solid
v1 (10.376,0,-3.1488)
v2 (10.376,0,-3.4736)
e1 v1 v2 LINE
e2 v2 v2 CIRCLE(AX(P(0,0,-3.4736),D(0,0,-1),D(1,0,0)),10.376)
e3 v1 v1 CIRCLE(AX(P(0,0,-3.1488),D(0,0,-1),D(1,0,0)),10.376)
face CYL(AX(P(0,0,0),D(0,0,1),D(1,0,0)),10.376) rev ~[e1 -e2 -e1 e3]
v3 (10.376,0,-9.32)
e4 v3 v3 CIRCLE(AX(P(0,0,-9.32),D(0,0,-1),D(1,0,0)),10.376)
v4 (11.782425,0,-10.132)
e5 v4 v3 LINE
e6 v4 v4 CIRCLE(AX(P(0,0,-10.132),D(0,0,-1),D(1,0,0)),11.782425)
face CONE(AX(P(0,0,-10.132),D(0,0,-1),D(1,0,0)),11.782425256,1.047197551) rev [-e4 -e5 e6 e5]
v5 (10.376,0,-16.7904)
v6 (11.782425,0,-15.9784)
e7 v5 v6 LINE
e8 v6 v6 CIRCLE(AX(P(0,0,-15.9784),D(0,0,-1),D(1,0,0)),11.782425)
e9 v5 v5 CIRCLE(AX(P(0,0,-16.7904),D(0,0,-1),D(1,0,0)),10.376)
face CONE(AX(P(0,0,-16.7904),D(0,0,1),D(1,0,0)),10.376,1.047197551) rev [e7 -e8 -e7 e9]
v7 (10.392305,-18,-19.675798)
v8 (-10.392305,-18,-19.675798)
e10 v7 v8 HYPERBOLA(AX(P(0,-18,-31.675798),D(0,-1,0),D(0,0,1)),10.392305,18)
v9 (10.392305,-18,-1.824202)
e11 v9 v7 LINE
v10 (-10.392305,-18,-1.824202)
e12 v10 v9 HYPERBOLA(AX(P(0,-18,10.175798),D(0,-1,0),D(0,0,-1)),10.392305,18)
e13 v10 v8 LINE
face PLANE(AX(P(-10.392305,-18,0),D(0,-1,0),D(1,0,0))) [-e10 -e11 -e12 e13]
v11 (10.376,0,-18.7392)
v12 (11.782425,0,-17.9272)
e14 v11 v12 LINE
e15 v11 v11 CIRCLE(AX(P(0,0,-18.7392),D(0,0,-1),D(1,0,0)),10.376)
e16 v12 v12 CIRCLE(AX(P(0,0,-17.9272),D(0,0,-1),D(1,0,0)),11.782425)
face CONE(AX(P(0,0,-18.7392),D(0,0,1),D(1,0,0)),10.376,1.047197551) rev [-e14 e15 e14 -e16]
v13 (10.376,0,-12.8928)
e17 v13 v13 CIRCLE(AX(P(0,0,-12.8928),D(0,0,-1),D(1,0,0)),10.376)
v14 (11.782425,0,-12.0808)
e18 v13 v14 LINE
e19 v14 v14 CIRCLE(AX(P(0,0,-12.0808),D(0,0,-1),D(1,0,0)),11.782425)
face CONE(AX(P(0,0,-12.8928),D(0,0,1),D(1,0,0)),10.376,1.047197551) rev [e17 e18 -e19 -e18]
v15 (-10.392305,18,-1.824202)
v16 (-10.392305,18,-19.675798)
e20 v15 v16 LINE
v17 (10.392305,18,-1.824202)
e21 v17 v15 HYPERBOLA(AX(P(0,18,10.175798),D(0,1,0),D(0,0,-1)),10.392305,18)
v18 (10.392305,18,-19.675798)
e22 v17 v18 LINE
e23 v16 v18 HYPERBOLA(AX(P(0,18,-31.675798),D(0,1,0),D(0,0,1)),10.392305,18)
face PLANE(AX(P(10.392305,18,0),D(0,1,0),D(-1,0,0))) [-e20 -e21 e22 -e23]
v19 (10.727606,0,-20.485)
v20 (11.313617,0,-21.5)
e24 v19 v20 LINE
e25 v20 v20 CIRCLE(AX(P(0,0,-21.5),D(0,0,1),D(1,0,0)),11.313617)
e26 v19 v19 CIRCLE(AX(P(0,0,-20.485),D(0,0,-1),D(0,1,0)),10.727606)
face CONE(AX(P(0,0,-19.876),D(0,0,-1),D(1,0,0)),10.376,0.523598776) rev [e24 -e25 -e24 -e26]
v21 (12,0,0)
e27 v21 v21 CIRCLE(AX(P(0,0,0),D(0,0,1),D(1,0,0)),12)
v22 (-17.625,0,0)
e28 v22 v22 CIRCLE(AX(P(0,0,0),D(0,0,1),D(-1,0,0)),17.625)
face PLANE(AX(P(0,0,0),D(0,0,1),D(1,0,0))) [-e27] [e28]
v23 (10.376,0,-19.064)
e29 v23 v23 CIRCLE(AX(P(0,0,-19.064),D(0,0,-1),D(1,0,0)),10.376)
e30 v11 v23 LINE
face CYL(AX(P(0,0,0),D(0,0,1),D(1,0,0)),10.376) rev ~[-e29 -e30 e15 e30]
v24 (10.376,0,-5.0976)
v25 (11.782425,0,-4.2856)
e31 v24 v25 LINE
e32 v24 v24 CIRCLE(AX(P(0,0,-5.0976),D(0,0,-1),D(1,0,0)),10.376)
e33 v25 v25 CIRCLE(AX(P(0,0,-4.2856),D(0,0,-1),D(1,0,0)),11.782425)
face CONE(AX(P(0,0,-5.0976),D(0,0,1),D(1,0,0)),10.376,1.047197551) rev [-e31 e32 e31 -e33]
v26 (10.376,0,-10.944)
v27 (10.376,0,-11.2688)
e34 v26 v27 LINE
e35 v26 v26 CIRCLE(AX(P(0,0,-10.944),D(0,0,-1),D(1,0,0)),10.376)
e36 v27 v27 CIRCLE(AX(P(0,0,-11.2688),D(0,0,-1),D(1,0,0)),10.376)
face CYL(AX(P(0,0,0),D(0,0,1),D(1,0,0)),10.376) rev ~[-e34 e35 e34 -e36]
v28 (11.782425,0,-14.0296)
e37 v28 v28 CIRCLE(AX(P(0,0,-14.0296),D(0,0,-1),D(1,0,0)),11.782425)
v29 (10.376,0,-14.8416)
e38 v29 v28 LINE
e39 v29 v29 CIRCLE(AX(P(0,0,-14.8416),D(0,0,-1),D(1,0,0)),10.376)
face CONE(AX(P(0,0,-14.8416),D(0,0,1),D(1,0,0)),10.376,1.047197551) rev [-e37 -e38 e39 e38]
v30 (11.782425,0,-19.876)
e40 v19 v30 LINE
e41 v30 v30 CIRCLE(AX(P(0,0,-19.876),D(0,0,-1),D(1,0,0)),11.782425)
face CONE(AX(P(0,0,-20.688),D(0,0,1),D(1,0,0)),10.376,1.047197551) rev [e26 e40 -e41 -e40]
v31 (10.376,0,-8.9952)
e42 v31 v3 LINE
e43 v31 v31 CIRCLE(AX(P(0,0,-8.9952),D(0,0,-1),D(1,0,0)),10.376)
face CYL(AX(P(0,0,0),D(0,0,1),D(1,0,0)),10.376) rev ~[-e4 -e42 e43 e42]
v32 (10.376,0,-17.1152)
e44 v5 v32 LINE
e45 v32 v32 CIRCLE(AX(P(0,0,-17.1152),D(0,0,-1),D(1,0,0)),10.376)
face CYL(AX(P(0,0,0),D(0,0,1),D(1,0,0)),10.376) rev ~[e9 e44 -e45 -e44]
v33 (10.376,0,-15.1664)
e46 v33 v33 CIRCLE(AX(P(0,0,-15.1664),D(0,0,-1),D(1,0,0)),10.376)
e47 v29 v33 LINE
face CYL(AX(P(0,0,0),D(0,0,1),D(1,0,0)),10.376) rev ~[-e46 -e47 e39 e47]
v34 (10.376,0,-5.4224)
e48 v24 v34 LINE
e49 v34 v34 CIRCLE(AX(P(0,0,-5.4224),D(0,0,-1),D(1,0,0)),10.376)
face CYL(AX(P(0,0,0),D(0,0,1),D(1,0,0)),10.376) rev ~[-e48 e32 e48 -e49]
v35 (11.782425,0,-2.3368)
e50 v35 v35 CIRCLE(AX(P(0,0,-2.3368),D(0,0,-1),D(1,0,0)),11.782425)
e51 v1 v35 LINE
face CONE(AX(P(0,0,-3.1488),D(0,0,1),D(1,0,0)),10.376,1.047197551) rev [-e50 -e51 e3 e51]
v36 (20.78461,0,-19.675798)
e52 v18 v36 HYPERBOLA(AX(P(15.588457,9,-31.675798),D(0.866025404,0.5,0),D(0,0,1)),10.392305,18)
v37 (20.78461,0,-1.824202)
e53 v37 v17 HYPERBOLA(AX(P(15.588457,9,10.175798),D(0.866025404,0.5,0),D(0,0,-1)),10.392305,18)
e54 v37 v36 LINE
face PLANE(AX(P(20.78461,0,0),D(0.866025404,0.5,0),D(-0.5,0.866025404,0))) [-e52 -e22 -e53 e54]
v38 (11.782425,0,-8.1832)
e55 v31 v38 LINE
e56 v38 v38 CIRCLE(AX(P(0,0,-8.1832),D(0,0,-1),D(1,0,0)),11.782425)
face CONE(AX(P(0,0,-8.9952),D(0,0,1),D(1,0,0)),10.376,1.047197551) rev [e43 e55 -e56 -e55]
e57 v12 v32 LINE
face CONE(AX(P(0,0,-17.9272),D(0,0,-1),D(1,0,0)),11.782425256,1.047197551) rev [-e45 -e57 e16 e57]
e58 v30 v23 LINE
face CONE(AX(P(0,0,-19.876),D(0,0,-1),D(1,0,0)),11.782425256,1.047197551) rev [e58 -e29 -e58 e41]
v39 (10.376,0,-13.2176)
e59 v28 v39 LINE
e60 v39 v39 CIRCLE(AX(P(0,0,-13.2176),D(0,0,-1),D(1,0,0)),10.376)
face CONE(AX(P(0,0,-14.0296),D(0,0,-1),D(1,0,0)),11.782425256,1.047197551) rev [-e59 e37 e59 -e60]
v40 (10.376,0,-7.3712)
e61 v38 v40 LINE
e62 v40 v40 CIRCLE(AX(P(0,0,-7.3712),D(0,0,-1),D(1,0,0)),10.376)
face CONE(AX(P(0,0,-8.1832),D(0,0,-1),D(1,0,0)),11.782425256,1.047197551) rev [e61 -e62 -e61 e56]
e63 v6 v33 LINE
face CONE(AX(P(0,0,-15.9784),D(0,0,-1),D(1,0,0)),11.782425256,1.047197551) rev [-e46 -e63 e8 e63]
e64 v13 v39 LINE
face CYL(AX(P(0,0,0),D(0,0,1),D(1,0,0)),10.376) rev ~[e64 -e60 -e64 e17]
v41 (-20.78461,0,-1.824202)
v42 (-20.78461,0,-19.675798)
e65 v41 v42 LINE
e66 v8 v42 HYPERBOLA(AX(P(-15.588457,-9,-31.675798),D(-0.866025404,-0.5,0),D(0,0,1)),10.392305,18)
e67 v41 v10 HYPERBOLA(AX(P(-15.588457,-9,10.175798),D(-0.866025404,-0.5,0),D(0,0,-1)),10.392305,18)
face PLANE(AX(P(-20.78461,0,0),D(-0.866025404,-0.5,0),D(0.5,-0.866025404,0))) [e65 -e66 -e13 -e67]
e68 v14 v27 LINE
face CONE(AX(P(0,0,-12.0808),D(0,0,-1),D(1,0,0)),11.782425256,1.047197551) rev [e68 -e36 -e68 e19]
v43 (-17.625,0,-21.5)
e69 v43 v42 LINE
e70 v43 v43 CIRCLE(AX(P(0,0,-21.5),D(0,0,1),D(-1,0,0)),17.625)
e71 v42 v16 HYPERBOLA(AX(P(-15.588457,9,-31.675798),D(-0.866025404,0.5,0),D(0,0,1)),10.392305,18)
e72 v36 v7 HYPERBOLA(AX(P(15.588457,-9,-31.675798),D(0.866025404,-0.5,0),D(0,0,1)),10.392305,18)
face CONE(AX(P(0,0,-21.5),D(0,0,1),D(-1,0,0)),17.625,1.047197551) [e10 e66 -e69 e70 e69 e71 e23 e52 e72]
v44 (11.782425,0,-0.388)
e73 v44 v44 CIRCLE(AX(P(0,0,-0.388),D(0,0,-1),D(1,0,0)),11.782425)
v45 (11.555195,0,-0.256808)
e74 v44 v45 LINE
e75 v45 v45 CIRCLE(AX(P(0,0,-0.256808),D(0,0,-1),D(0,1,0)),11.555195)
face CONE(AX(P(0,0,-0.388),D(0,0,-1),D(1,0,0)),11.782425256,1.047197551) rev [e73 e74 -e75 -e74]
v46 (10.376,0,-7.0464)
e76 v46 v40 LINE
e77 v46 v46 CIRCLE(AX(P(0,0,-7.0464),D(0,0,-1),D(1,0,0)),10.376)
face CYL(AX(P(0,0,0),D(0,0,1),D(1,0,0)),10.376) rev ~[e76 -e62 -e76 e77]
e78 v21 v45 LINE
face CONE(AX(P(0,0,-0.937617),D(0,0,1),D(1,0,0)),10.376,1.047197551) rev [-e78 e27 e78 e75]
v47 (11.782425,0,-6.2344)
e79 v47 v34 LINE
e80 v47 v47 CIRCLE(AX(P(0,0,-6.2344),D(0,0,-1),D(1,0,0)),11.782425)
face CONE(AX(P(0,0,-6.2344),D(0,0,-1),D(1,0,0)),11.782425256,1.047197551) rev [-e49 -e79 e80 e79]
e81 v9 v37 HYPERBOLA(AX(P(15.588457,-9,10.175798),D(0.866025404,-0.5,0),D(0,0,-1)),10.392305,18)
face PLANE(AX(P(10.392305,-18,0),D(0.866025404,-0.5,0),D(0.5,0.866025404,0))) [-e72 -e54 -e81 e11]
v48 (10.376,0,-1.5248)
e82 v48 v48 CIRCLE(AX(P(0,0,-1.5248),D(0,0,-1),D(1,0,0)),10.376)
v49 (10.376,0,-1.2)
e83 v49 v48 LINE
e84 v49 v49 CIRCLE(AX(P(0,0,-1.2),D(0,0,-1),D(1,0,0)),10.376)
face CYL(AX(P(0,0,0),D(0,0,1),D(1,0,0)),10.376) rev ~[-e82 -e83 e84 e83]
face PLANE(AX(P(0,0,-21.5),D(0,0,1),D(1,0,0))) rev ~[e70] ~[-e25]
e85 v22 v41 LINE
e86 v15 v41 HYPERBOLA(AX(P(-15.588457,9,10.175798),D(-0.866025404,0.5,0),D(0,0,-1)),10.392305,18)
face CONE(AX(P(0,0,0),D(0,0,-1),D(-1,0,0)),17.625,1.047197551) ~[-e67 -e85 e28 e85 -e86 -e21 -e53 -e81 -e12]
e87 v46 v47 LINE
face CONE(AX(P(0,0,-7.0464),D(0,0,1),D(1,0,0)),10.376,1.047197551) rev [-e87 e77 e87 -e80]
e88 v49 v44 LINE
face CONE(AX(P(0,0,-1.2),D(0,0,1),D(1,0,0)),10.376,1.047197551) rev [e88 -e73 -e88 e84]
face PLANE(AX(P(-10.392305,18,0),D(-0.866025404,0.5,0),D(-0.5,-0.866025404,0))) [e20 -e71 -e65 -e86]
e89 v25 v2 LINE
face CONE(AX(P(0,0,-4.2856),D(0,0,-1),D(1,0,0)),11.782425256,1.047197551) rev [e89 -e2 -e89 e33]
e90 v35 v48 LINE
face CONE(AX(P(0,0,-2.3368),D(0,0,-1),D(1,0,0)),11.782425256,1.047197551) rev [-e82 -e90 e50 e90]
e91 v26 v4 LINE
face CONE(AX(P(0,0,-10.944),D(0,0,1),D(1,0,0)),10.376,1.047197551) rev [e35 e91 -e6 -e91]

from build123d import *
from OCP.BRepFilletAPI import BRepFilletAPI_MakeChamfer

# Parameters (mm, degrees)
SKETCH1_R        = 10.376
BASENUT_DEPTH    = 21.5
ENDCHAMFER_SIZE  = 1.624
ENDCHAMFER_SIZE2 = 0.937616837
LPATTERN10_COUNT = 11
LPATTERN10_PITCH = 1.9488


with BuildPart() as part:
    # Sketch1 → BaseNut (new body)
    with BuildSketch(Plane.XY):
        Polygon((20.784609691, 0), (10.392304845, 18), (-10.392304845, 18), (-20.784609691, 0), (-10.392304845, -18), (10.392304845, -18), align=None)
        Circle(SKETCH1_R, mode=Mode.SUBTRACT)
    extrude(amount=-BASENUT_DEPTH)

    # Sketch2 → Double-Chamfer (revolve, cut)
    with BuildSketch(Plane(origin=(0, 0, 0), x_dir=(1, 0, 0), z_dir=(0, 1, 0))):
        Polygon((-20.784609691, 21.5), (-17.625, 21.5), (-20.784609691, 19.675798494), align=None)
        Polygon((-20.784609691, 1.824201506), (-20.784609691, 0), (-17.625, 0), align=None)
    revolve(axis=Axis((0, 0, -3.375940562), (0, 0, 1)), mode=Mode.SUBTRACT)

    # EndChamfer: one chamfer whose edges measure the first distance from different faces: ONE call of the kernel's chamfer builder (chamfer() names one face for all edges)
    endchamfer_edges_1 = [part.edges().sort_by_distance(p)[0] for p in [
        (-10.376, 0, -21.5),
    ]]
    endchamfer_side_1 = [part.faces().sort_by_distance(p)[0] for p in [
        (-10.376, 0, -10.75),
    ]]
    endchamfer_edges_2 = [part.edges().sort_by_distance(p)[0] for p in [
        (-10.376, 0, 0),
    ]]
    endchamfer_side_2 = [part.faces().sort_by_distance(p)[0] for p in [
        (17.126489719, 0, 0),
    ]]
    endchamfer = BRepFilletAPI_MakeChamfer(part.part.solid().wrapped)
    for e in endchamfer_edges_1:
        endchamfer.Add(ENDCHAMFER_SIZE, ENDCHAMFER_SIZE2, e.wrapped, endchamfer_side_1[0].wrapped)  # the first distance lies on this face
    for e in endchamfer_edges_2:
        endchamfer.Add(ENDCHAMFER_SIZE, ENDCHAMFER_SIZE2, e.wrapped, endchamfer_side_2[0].wrapped)  # the first distance lies on this face
    add(Compound.cast(endchamfer.Shape()), mode=Mode.REPLACE)

    # Sketch3 → Cut-Revolve10 (revolve, cut)
    with BuildSketch(Plane(origin=(0, 0, 0), x_dir=(1, 0, 0), z_dir=(0, 1, 0)), mode=Mode.PRIVATE) as cut_revolve10_sk:
        Polygon((-11.782425256, 19.876), (-10.376, 19.064), (-8.752, 19.064), (-8.752, 20.688), (-10.376, 20.688), align=None)
    cut_revolve10 = revolve(cut_revolve10_sk.sketch.rotate(Axis((0, 0, -7.438254559), (0, 0, -1)), 180), axis=Axis((0, 0, -7.438254559), (0, 0, -1)), mode=Mode.SUBTRACT)

    # LPattern10: Cut-Revolve10 ×11
    with Locations(*[(0, 0, i * LPATTERN10_PITCH) for i in range(1, LPATTERN10_COUNT)]):
        add(cut_revolve10, mode=Mode.SUBTRACT)


solid = part.part
